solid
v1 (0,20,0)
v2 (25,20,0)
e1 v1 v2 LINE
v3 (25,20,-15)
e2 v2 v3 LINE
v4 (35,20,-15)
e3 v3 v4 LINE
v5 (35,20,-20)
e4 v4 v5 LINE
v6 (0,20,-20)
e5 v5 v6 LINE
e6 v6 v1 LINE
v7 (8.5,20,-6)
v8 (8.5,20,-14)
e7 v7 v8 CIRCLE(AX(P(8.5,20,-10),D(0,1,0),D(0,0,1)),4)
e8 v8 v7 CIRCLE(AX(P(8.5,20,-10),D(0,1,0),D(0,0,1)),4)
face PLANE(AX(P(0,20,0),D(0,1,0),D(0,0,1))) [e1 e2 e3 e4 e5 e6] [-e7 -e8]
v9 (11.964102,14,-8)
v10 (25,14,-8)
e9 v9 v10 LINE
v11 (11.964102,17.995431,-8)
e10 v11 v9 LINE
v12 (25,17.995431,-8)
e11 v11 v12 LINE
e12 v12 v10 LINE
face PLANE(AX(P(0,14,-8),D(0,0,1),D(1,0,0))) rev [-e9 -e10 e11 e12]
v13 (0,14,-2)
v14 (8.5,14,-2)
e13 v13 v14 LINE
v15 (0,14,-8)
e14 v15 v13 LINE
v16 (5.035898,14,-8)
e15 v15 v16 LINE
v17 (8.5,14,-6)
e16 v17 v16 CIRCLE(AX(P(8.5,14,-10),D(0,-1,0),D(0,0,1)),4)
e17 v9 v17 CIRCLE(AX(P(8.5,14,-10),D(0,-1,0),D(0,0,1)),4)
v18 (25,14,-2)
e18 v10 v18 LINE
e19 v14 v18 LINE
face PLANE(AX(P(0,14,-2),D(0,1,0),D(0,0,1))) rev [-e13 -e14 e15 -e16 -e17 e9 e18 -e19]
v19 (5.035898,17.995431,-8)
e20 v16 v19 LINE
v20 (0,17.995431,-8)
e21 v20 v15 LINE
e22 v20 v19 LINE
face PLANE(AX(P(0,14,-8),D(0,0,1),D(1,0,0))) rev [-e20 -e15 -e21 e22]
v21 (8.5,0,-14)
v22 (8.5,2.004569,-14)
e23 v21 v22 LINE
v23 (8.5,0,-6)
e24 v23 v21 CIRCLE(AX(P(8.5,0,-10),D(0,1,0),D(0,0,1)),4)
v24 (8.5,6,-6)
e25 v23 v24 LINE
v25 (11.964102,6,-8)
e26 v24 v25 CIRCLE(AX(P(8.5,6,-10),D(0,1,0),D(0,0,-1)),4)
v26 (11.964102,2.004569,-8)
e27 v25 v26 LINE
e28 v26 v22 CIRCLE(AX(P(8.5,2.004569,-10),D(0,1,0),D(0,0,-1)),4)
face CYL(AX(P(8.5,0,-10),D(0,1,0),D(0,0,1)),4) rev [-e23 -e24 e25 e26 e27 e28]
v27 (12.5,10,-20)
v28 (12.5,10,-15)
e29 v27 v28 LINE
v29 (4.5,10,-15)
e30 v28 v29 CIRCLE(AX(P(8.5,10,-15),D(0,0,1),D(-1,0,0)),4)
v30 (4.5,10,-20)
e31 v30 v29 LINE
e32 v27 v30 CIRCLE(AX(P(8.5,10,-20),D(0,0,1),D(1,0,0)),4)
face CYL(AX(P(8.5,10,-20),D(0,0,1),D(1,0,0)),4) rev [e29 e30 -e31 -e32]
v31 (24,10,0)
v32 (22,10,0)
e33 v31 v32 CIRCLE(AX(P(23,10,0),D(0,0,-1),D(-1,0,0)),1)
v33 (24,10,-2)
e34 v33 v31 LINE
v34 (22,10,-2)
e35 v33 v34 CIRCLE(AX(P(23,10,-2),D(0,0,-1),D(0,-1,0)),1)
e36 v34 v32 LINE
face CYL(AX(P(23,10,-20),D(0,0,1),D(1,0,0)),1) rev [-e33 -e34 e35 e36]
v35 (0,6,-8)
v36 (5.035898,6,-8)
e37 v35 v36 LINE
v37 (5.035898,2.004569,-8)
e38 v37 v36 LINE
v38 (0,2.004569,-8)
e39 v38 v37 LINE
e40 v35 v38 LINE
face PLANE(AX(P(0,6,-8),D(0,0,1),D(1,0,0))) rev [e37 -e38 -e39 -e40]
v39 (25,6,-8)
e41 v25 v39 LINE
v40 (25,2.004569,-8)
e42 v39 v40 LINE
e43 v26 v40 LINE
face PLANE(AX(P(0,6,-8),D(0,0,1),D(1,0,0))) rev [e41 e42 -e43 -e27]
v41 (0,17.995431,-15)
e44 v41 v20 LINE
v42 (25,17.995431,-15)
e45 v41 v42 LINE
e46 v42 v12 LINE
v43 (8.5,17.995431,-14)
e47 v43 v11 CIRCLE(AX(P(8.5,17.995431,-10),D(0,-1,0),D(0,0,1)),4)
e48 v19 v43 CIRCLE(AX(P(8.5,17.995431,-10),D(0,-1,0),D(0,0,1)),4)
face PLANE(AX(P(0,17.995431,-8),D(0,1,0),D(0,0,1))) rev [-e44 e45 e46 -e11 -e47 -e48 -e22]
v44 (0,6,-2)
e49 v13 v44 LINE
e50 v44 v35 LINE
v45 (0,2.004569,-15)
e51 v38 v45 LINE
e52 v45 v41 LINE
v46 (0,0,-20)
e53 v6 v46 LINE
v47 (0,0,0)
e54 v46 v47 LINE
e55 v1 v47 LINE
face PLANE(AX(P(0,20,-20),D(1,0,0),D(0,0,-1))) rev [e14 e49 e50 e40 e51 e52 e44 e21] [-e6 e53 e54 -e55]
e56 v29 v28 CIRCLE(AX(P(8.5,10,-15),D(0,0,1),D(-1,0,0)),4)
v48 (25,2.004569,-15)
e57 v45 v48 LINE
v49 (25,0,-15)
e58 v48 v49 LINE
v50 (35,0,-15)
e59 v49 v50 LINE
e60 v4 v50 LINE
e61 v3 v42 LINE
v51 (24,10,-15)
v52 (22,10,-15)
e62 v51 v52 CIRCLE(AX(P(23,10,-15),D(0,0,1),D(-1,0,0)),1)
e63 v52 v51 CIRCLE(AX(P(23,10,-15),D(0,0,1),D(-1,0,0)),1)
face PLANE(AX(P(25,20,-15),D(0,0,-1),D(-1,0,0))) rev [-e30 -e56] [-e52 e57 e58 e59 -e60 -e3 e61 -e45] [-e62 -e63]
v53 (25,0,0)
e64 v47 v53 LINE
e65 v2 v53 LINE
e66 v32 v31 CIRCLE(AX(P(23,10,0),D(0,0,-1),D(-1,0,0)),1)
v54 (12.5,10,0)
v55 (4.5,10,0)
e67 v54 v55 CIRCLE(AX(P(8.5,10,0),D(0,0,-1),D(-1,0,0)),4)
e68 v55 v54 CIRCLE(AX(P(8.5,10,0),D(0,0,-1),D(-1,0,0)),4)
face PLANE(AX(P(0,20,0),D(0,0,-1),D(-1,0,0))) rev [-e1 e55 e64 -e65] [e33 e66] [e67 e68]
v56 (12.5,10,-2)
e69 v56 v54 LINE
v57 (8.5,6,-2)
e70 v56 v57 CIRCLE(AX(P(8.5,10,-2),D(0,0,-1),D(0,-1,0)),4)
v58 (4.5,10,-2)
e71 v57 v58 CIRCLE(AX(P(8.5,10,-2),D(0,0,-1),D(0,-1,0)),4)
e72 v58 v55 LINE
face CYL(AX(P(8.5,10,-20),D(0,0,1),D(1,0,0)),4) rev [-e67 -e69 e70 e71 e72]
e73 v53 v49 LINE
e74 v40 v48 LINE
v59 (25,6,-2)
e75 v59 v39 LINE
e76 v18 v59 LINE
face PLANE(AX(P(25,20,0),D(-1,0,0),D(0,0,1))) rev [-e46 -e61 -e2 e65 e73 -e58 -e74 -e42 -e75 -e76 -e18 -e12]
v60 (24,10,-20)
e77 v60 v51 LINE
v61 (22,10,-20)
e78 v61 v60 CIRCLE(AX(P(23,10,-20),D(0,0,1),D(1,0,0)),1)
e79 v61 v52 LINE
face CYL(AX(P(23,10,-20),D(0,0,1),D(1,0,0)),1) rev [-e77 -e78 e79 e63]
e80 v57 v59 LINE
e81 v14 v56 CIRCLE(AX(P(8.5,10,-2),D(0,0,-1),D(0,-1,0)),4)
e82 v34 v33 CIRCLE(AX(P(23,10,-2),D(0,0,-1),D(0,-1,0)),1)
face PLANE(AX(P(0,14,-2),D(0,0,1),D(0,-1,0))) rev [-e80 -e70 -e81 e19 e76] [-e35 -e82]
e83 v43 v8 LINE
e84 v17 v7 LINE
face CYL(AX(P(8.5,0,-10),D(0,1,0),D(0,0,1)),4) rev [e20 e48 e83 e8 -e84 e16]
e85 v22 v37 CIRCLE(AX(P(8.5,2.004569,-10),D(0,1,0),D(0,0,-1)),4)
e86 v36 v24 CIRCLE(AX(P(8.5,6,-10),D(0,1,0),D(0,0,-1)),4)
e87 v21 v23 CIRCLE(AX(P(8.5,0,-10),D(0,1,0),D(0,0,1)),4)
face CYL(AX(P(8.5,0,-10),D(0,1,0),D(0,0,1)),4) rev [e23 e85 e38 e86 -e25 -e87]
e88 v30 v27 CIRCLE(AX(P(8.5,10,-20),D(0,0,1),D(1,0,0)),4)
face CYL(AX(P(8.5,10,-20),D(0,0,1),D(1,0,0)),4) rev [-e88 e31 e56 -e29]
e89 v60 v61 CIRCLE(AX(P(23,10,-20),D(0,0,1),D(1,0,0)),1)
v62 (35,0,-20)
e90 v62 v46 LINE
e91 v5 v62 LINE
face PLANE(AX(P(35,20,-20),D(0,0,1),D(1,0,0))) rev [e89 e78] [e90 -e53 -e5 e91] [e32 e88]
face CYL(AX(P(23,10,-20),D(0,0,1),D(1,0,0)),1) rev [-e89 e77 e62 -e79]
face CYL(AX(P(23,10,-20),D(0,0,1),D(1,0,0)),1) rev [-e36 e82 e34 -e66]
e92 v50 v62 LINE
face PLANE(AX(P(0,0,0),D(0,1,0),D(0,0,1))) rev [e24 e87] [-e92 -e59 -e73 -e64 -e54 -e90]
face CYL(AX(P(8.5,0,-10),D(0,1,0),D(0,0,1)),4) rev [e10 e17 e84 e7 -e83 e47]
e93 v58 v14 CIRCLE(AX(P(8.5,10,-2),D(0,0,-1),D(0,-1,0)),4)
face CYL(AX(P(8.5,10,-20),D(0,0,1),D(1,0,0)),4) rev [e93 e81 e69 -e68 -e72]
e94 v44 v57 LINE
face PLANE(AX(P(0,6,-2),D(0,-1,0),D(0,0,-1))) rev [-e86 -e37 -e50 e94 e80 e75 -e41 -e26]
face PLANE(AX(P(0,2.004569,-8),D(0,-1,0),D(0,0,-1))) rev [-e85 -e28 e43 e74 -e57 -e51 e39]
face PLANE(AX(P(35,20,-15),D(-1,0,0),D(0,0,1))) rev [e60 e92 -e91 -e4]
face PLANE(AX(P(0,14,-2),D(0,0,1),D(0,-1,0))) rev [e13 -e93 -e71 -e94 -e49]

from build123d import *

# Parameters (mm, degrees)
BOSS_EXTRUDE1_DEPTH     = 20
CUT_EXTRUDE1_DEPTH      = 46
CUT_EXTRUDE1_DEPTH_BACK = 46
SKETCH2_R               = 4
SKETCH2_R_2             = 1
CUT_EXTRUDE3_DEPTH      = 46
CUT_EXTRUDE3_DEPTH_BACK = 46
SKETCH5_R               = 4
CUT_EXTRUDE4_DEPTH      = 38.749172176


with BuildPart() as part:
    # Sketch1 → Boss-Extrude1 (new body)
    with BuildSketch(Plane(origin=(0, 0, 0), x_dir=(1, 0, 0), z_dir=(0, 1, 0))):
        Polygon((0, 0), (25, 0), (25, 15), (35, 15), (35, 20), (0, 20), align=None)
    extrude(amount=BOSS_EXTRUDE1_DEPTH)

    # Sketch2 → Cut-Extrude1 (cut, two sides: drawn at the far end of the back side and taken through both)
    with BuildSketch(Plane.XY.offset(-CUT_EXTRUDE1_DEPTH_BACK)):
        with Locations((8.5, 10)):
            Circle(SKETCH2_R)
        with Locations((23, 10)):
            Circle(SKETCH2_R_2)
    extrude(amount=CUT_EXTRUDE1_DEPTH + CUT_EXTRUDE1_DEPTH_BACK, mode=Mode.SUBTRACT)

    # Sketch5 → Cut-Extrude3 (cut, two sides: drawn at the far end of the back side and taken through both)
    with BuildSketch(Plane(origin=(0, 20, 0), x_dir=(1, 0, 0), z_dir=(0, 1, 0)).offset(-CUT_EXTRUDE3_DEPTH_BACK)):
        with Locations(Location((8.5, 10, 0), (0, 0, 270))):
            Circle(SKETCH5_R)
    extrude(amount=CUT_EXTRUDE3_DEPTH + CUT_EXTRUDE3_DEPTH_BACK, mode=Mode.SUBTRACT)

    # Sketch6 → Cut-Extrude4 (cut, through all)
    with BuildSketch(Plane(origin=(25, 0, 0), x_dir=(0, 0, -1), z_dir=(1, 0, 0))):
        Polygon((2, 14), (2, 6), (8, 6), (8, 2.004568818), (15, 2.004568818), (15, 17.995431182), (8, 17.995431182), (8, 14), align=None)
    extrude(amount=-CUT_EXTRUDE4_DEPTH, mode=Mode.SUBTRACT)


solid = part.part
